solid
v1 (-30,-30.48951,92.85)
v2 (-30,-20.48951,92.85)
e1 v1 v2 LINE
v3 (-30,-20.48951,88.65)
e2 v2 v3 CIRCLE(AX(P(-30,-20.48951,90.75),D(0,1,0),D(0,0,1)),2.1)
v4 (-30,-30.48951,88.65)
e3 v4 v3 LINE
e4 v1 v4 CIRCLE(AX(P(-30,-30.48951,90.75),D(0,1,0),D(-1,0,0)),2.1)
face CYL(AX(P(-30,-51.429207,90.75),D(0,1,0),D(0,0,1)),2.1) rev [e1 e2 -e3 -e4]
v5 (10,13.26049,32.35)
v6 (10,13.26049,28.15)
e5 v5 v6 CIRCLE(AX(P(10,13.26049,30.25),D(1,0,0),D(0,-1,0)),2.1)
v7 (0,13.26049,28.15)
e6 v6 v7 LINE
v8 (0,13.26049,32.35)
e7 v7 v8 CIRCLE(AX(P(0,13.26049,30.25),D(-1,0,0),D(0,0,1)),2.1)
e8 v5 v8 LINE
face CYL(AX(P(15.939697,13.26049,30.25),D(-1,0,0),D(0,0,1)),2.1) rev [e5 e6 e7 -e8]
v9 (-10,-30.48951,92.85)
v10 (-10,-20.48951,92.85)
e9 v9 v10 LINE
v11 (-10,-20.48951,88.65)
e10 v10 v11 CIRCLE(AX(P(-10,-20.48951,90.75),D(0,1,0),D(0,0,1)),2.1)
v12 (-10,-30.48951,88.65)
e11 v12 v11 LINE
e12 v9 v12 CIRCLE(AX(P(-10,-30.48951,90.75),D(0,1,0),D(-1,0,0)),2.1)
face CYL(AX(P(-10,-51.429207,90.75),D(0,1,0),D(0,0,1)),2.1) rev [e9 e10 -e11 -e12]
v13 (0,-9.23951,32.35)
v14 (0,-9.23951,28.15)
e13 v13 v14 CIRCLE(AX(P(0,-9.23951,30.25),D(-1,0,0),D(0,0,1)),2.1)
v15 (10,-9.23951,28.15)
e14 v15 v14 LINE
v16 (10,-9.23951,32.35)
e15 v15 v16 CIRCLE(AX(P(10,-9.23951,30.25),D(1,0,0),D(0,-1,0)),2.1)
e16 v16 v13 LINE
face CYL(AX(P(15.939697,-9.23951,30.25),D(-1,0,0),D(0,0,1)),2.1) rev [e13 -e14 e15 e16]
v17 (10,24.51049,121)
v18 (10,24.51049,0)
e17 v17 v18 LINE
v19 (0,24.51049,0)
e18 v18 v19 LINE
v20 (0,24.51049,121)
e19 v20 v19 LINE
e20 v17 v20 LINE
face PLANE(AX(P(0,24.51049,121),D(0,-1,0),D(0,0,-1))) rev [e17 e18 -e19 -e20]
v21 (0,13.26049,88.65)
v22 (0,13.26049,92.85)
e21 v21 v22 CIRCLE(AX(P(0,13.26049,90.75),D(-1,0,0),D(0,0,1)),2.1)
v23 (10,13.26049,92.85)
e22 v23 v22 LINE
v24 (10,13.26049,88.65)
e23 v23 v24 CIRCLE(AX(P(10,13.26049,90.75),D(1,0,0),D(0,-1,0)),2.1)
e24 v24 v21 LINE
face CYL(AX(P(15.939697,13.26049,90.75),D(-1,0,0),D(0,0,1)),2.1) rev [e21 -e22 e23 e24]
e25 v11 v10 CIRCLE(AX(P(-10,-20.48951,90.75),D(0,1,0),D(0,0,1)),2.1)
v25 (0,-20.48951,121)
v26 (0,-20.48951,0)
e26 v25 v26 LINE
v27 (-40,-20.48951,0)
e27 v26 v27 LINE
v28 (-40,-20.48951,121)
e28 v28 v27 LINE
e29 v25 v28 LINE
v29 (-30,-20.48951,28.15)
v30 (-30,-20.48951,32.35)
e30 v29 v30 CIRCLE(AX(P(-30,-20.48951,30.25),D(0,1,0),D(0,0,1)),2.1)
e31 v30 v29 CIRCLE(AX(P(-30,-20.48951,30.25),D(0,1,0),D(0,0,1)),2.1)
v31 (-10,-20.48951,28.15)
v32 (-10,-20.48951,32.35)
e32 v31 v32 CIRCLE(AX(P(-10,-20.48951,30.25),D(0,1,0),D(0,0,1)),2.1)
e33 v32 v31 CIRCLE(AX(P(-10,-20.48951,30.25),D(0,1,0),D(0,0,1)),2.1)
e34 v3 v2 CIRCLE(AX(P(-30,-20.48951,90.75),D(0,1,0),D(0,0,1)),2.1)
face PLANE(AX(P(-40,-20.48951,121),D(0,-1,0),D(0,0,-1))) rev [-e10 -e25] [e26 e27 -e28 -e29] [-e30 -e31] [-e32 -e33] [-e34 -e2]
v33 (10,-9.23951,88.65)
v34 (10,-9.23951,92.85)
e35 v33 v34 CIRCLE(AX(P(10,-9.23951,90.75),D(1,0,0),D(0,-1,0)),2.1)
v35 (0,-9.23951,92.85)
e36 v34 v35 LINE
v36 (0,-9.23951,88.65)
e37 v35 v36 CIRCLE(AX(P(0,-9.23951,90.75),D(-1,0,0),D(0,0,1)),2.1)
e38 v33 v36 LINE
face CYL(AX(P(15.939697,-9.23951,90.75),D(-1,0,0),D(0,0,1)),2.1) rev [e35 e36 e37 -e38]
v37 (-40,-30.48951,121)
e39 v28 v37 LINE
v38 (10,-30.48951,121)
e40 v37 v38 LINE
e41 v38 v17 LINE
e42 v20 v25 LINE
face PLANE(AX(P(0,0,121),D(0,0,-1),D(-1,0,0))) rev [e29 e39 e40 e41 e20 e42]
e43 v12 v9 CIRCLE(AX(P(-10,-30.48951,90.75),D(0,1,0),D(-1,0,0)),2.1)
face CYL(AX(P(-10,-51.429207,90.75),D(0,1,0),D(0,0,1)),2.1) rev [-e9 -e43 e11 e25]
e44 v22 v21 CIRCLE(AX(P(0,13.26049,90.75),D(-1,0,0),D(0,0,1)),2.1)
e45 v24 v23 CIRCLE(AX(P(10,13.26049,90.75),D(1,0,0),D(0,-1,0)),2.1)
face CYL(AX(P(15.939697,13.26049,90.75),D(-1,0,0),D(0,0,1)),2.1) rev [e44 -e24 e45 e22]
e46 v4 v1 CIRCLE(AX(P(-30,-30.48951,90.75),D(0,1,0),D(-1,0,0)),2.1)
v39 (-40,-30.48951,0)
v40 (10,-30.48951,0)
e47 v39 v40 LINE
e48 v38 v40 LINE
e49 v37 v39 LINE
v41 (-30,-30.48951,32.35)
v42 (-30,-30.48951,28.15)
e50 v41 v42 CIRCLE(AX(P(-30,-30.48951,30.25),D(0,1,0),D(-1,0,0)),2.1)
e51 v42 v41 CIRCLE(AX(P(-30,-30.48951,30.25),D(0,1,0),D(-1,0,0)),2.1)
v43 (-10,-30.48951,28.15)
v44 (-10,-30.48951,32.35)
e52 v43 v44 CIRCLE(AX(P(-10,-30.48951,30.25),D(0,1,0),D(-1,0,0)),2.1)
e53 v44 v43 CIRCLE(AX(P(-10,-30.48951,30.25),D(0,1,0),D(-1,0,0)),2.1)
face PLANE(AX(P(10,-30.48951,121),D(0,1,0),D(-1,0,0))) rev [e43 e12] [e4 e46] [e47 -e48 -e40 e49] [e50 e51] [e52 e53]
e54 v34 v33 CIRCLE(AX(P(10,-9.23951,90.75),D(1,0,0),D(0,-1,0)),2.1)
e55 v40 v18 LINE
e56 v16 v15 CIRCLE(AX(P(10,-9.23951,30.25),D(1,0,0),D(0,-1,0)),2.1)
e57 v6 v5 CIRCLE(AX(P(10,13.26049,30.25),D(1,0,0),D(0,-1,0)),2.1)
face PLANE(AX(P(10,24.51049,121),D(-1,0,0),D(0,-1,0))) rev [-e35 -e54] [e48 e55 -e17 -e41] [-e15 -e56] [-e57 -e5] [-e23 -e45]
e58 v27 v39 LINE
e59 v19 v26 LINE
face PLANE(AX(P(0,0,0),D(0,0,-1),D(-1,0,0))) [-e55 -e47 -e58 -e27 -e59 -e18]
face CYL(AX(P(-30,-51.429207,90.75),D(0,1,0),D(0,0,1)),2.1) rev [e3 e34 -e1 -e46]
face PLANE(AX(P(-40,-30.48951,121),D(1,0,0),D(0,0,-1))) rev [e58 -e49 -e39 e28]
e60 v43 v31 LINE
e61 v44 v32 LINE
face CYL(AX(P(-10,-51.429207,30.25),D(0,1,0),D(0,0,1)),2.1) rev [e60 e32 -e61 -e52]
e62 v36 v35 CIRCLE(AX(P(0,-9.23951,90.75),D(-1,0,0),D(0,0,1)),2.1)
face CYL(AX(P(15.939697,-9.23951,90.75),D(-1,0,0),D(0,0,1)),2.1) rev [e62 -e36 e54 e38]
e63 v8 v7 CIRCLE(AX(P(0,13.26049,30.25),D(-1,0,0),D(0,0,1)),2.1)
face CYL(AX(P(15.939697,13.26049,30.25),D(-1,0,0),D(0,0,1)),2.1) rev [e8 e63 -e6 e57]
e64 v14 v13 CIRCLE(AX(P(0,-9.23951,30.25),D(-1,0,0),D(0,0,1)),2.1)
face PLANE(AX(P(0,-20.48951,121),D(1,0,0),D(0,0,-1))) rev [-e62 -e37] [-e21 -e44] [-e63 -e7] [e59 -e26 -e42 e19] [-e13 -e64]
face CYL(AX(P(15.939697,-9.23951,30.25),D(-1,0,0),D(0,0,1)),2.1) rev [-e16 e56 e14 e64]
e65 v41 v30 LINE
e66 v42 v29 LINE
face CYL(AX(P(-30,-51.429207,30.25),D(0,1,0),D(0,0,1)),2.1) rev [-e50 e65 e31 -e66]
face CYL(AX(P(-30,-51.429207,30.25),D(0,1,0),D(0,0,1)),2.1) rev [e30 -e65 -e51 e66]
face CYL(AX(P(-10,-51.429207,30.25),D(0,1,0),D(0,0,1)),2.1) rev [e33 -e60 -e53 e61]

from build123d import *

# Parameters (mm, degrees)
EXTRUDE_1_DEPTH     = 121
CUT_EXTRUDE_2_REACH = 1320.001
SKETCH_3_R          = 2.099999998
SKETCH_3_R_2        = 2.100000002
SKETCH_5_R          = 2.1
CUT_EXTRUDE_3_DEPTH = 10


with BuildPart() as part:
    # 草图1 → 凸台-拉伸1 (new body)
    with BuildSketch(Plane.XY):
        Polygon((0, 24.51048951), (10, 24.51048951), (10, -30.48951049), (-40, -30.48951049), (-40, -20.48951049), (0, -20.48951049), align=None)
    extrude(amount=EXTRUDE_1_DEPTH)

    # 草图3 → 切除-拉伸2 (cut, up to next)
    with BuildSketch(Plane(origin=(-858.744003867, -20.48951049, -869.143932912), x_dir=(-1, 0, 0), z_dir=(0, 1, 0)), mode=Mode.PRIVATE) as cut_extrude_2_sk1:
        with Locations(Location((-848.744003867, 959.893932917, 0), (0, 0, 90))):
            Circle(SKETCH_3_R)
    cut_extrude_2_tool1 = extrude(cut_extrude_2_sk1.sketch, amount=-CUT_EXTRUDE_2_REACH, mode=Mode.PRIVATE) & part.part
    # 草图3 → 切除-拉伸2 (cut, up to next)
    with BuildSketch(Plane(origin=(-858.744003867, -20.48951049, -869.143932912), x_dir=(-1, 0, 0), z_dir=(0, 1, 0)), mode=Mode.PRIVATE) as cut_extrude_2_sk2:
        with Locations(Location((-828.744003867, 959.893932906, 0), (0, 0, 90))):
            Circle(SKETCH_3_R_2)
    cut_extrude_2_tool2 = extrude(cut_extrude_2_sk2.sketch, amount=-CUT_EXTRUDE_2_REACH, mode=Mode.PRIVATE) & part.part
    # 草图3 → 切除-拉伸2 (cut, up to next)
    with BuildSketch(Plane(origin=(-858.744003867, -20.48951049, -869.143932912), x_dir=(-1, 0, 0), z_dir=(0, 1, 0)), mode=Mode.PRIVATE) as cut_extrude_2_sk3:
        with Locations(Location((-828.744003867, 899.393932906, 0), (0, 0, 90))):
            Circle(SKETCH_3_R_2)
    cut_extrude_2_tool3 = extrude(cut_extrude_2_sk3.sketch, amount=-CUT_EXTRUDE_2_REACH, mode=Mode.PRIVATE) & part.part
    # 草图3 → 切除-拉伸2 (cut, up to next)
    with BuildSketch(Plane(origin=(-858.744003867, -20.48951049, -869.143932912), x_dir=(-1, 0, 0), z_dir=(0, 1, 0)), mode=Mode.PRIVATE) as cut_extrude_2_sk4:
        with Locations(Location((-848.744003867, 899.393932906, 0), (0, 0, 90))):
            Circle(SKETCH_3_R_2)
    cut_extrude_2_tool4 = extrude(cut_extrude_2_sk4.sketch, amount=-CUT_EXTRUDE_2_REACH, mode=Mode.PRIVATE) & part.part
    add(cut_extrude_2_tool1.solids().sort_by_distance((-10, -20.48951, 90.75))[0], mode=Mode.SUBTRACT)
    add(cut_extrude_2_tool2.solids().sort_by_distance((-30, -20.48951, 90.75))[0], mode=Mode.SUBTRACT)
    add(cut_extrude_2_tool3.solids().sort_by_distance((-30, -20.48951, 30.25))[0], mode=Mode.SUBTRACT)
    add(cut_extrude_2_tool4.solids().sort_by_distance((-10, -20.48951, 30.25))[0], mode=Mode.SUBTRACT)

    # 草图5 → 切除-拉伸3 (cut)
    with BuildSketch(Plane.ZY):
        with Locations((30.250000004, 13.26048951)):
            Circle(SKETCH_5_R)
        with Locations((30.250000004, -9.23951049)):
            Circle(SKETCH_5_R)
        with Locations((90.750000004, 13.26048951)):
            Circle(SKETCH_5_R)
        with Locations((90.750000004, -9.23951049)):
            Circle(SKETCH_5_R)
    extrude(amount=-CUT_EXTRUDE_3_DEPTH, mode=Mode.SUBTRACT)


solid = part.part
